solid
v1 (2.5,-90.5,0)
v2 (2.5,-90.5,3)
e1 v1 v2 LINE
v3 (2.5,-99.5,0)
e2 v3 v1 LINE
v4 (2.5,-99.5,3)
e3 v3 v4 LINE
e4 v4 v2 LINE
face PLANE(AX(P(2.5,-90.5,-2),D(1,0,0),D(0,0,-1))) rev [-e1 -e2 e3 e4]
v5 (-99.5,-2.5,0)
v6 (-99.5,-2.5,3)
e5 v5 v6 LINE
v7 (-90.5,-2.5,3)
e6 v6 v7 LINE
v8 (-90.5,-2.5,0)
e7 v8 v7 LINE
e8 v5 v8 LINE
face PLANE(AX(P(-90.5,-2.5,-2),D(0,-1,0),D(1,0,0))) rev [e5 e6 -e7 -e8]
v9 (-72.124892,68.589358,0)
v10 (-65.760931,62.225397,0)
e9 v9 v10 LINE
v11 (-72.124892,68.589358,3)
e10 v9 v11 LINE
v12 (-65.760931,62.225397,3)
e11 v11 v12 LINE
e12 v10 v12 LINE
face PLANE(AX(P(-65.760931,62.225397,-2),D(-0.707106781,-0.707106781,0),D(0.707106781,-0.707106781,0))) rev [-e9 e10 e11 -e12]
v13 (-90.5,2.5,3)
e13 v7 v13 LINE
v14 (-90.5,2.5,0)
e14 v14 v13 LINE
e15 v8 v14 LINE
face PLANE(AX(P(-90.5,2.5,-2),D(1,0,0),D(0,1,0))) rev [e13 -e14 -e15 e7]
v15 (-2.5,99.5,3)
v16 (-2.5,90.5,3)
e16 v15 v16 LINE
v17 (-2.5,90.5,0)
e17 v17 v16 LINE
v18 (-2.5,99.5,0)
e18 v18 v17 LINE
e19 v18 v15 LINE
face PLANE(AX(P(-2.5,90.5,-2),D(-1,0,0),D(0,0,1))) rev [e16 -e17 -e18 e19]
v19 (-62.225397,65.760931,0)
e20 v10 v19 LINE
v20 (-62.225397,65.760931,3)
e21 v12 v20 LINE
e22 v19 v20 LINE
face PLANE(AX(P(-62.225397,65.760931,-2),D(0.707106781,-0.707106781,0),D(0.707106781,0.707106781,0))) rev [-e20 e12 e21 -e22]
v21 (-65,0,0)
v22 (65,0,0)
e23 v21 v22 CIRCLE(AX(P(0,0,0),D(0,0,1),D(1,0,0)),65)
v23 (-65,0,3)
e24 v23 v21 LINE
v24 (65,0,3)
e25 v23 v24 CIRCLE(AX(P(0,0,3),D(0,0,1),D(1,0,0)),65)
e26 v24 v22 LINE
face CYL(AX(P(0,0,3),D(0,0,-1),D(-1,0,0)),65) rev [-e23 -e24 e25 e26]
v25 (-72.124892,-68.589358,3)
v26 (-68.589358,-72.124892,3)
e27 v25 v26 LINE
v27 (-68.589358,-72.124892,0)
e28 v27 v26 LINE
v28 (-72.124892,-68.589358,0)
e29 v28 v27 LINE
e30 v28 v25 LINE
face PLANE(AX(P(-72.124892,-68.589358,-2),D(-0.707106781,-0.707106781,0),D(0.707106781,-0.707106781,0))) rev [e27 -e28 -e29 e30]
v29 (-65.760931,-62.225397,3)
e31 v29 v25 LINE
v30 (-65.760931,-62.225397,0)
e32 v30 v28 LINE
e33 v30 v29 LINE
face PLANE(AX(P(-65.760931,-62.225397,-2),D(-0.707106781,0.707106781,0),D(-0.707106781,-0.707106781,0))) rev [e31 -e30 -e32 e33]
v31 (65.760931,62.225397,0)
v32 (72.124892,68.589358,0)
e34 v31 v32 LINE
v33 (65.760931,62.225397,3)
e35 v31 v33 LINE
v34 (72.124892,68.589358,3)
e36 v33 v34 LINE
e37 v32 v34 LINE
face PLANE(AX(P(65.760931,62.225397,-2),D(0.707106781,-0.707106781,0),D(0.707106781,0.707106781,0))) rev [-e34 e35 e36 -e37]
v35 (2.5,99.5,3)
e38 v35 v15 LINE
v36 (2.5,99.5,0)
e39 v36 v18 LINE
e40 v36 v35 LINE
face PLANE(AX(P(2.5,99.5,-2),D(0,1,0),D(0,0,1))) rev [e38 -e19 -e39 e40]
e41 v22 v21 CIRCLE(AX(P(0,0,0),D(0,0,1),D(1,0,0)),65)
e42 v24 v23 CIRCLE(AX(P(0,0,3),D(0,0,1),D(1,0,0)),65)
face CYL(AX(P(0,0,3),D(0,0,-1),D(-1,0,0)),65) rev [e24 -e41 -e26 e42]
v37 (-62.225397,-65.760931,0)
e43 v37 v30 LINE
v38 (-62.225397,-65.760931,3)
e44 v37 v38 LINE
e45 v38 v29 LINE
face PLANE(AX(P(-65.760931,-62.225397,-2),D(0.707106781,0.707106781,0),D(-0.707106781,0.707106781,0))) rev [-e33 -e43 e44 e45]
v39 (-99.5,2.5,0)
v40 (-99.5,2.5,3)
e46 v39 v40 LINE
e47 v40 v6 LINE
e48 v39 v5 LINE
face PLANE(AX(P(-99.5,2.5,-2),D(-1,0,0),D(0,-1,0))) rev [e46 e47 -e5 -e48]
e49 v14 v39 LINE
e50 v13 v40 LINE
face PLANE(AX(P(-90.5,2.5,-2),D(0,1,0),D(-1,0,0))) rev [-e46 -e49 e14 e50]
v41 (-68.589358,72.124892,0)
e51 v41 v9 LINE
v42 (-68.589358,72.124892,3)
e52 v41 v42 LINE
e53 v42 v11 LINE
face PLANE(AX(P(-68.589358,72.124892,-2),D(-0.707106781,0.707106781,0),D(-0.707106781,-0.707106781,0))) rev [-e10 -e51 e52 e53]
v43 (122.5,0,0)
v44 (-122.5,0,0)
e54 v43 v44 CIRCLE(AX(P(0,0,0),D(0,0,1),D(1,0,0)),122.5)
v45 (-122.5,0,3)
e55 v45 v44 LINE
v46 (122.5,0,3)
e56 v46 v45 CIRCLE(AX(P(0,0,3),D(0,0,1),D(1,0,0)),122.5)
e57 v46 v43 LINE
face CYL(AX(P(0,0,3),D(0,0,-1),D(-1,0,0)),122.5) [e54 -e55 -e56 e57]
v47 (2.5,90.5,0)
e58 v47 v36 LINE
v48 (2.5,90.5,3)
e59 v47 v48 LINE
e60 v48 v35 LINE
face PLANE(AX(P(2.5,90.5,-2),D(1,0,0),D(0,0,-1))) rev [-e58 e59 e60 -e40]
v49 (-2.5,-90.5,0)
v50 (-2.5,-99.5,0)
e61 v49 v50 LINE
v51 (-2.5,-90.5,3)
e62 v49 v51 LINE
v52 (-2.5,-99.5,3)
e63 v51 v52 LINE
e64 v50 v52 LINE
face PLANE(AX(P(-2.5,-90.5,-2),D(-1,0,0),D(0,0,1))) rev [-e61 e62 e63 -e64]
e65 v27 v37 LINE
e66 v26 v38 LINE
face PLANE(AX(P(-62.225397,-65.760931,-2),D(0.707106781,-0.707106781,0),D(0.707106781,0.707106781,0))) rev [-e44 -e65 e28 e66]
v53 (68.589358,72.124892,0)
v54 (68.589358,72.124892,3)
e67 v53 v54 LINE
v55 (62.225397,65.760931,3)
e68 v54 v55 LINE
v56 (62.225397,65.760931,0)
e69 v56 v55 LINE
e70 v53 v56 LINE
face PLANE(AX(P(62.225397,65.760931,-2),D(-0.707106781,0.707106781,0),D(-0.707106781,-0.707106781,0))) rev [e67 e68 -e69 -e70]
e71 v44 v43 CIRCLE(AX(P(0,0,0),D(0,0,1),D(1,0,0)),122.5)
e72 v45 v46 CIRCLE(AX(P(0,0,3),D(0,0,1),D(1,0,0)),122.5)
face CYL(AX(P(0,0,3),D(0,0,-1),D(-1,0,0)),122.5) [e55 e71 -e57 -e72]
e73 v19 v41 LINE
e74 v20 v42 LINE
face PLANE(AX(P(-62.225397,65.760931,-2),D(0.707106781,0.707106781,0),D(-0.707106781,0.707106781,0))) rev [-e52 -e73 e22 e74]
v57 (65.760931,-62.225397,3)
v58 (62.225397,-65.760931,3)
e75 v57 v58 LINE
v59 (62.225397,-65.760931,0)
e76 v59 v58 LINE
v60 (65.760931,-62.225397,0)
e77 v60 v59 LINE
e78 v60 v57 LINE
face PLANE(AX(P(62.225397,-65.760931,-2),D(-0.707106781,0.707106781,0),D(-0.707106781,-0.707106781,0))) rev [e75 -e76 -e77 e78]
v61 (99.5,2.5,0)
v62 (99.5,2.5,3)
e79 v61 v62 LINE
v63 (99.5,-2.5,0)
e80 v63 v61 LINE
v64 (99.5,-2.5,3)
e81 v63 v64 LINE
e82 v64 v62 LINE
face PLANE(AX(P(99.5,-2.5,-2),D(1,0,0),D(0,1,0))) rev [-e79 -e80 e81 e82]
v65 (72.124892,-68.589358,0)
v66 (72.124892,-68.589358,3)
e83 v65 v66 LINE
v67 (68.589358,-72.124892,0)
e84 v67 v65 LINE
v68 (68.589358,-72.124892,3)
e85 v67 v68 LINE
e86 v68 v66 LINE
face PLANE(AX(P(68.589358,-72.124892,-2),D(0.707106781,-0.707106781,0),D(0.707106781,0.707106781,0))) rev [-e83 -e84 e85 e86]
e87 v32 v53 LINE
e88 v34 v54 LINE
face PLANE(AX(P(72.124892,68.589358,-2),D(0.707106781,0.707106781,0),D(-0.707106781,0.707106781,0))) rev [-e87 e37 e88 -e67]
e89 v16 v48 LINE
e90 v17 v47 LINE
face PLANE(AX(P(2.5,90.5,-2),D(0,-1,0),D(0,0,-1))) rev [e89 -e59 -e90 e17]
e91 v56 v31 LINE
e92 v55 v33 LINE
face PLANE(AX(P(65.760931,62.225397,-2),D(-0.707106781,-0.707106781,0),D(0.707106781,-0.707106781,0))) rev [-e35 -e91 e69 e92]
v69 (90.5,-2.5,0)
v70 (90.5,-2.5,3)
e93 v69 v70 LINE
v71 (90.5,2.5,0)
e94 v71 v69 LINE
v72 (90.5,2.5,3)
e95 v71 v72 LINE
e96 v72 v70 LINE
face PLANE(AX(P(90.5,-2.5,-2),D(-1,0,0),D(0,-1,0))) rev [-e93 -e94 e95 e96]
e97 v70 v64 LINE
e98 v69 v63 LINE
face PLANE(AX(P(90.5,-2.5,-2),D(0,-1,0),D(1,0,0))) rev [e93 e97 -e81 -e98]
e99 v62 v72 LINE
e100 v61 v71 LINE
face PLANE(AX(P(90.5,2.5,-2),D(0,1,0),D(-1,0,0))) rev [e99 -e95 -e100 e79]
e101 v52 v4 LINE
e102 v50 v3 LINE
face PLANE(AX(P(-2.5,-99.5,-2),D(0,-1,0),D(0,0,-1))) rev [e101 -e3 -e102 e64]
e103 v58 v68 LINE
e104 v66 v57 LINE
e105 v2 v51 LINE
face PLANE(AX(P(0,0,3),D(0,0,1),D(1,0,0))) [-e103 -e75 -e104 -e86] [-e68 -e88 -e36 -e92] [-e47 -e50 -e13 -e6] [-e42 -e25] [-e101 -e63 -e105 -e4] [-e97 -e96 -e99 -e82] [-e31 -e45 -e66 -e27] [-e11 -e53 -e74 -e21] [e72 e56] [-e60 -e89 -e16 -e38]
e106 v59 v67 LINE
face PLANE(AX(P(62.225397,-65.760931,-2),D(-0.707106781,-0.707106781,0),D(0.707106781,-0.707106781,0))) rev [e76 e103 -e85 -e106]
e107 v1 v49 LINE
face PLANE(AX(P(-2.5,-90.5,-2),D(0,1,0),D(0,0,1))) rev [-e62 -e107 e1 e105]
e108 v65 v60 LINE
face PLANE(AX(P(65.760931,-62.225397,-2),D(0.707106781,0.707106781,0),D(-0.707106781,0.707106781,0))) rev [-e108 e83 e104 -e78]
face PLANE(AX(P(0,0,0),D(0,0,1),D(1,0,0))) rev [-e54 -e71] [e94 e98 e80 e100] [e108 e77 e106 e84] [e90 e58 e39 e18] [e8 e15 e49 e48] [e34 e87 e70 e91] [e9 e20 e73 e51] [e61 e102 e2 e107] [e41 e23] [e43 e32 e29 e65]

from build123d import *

# Parameters (mm, degrees)
SKETCH_1_R               = 122.5
SKETCH_1_R_2             = 65
EXTRUDE_1_DEPTH          = 3
SKETCH_2_W               = 5
SKETCH_2_H               = 9
CUT_EXTRUDE_1_DEPTH      = 5
PATTERN_CIRCULAR_1_COUNT = 8


with BuildPart() as part:
    # 草图1 → 凸台-拉伸1 (new body)
    with BuildSketch(Plane.XY):
        Circle(SKETCH_1_R)
        Circle(SKETCH_1_R_2, mode=Mode.SUBTRACT)
    extrude(amount=EXTRUDE_1_DEPTH)

    # 草图2 → 切除-拉伸1 (cut)
    with BuildSketch(Plane.XY.offset(3)):
        with Locations((0, 95)):
            Rectangle(SKETCH_2_W, SKETCH_2_H)
    cut_extrude_1 = extrude(amount=-CUT_EXTRUDE_1_DEPTH, mode=Mode.SUBTRACT)

    # 阵列(圆周)1: 切除-拉伸1 ×8 about axis
    pattern_circular_1_axis = Axis((0, 0, 0), (0, 0, 1))
    for i in range(1, PATTERN_CIRCULAR_1_COUNT):
        add(cut_extrude_1.rotate(pattern_circular_1_axis, i * 360 / PATTERN_CIRCULAR_1_COUNT), mode=Mode.SUBTRACT)


solid = part.part
